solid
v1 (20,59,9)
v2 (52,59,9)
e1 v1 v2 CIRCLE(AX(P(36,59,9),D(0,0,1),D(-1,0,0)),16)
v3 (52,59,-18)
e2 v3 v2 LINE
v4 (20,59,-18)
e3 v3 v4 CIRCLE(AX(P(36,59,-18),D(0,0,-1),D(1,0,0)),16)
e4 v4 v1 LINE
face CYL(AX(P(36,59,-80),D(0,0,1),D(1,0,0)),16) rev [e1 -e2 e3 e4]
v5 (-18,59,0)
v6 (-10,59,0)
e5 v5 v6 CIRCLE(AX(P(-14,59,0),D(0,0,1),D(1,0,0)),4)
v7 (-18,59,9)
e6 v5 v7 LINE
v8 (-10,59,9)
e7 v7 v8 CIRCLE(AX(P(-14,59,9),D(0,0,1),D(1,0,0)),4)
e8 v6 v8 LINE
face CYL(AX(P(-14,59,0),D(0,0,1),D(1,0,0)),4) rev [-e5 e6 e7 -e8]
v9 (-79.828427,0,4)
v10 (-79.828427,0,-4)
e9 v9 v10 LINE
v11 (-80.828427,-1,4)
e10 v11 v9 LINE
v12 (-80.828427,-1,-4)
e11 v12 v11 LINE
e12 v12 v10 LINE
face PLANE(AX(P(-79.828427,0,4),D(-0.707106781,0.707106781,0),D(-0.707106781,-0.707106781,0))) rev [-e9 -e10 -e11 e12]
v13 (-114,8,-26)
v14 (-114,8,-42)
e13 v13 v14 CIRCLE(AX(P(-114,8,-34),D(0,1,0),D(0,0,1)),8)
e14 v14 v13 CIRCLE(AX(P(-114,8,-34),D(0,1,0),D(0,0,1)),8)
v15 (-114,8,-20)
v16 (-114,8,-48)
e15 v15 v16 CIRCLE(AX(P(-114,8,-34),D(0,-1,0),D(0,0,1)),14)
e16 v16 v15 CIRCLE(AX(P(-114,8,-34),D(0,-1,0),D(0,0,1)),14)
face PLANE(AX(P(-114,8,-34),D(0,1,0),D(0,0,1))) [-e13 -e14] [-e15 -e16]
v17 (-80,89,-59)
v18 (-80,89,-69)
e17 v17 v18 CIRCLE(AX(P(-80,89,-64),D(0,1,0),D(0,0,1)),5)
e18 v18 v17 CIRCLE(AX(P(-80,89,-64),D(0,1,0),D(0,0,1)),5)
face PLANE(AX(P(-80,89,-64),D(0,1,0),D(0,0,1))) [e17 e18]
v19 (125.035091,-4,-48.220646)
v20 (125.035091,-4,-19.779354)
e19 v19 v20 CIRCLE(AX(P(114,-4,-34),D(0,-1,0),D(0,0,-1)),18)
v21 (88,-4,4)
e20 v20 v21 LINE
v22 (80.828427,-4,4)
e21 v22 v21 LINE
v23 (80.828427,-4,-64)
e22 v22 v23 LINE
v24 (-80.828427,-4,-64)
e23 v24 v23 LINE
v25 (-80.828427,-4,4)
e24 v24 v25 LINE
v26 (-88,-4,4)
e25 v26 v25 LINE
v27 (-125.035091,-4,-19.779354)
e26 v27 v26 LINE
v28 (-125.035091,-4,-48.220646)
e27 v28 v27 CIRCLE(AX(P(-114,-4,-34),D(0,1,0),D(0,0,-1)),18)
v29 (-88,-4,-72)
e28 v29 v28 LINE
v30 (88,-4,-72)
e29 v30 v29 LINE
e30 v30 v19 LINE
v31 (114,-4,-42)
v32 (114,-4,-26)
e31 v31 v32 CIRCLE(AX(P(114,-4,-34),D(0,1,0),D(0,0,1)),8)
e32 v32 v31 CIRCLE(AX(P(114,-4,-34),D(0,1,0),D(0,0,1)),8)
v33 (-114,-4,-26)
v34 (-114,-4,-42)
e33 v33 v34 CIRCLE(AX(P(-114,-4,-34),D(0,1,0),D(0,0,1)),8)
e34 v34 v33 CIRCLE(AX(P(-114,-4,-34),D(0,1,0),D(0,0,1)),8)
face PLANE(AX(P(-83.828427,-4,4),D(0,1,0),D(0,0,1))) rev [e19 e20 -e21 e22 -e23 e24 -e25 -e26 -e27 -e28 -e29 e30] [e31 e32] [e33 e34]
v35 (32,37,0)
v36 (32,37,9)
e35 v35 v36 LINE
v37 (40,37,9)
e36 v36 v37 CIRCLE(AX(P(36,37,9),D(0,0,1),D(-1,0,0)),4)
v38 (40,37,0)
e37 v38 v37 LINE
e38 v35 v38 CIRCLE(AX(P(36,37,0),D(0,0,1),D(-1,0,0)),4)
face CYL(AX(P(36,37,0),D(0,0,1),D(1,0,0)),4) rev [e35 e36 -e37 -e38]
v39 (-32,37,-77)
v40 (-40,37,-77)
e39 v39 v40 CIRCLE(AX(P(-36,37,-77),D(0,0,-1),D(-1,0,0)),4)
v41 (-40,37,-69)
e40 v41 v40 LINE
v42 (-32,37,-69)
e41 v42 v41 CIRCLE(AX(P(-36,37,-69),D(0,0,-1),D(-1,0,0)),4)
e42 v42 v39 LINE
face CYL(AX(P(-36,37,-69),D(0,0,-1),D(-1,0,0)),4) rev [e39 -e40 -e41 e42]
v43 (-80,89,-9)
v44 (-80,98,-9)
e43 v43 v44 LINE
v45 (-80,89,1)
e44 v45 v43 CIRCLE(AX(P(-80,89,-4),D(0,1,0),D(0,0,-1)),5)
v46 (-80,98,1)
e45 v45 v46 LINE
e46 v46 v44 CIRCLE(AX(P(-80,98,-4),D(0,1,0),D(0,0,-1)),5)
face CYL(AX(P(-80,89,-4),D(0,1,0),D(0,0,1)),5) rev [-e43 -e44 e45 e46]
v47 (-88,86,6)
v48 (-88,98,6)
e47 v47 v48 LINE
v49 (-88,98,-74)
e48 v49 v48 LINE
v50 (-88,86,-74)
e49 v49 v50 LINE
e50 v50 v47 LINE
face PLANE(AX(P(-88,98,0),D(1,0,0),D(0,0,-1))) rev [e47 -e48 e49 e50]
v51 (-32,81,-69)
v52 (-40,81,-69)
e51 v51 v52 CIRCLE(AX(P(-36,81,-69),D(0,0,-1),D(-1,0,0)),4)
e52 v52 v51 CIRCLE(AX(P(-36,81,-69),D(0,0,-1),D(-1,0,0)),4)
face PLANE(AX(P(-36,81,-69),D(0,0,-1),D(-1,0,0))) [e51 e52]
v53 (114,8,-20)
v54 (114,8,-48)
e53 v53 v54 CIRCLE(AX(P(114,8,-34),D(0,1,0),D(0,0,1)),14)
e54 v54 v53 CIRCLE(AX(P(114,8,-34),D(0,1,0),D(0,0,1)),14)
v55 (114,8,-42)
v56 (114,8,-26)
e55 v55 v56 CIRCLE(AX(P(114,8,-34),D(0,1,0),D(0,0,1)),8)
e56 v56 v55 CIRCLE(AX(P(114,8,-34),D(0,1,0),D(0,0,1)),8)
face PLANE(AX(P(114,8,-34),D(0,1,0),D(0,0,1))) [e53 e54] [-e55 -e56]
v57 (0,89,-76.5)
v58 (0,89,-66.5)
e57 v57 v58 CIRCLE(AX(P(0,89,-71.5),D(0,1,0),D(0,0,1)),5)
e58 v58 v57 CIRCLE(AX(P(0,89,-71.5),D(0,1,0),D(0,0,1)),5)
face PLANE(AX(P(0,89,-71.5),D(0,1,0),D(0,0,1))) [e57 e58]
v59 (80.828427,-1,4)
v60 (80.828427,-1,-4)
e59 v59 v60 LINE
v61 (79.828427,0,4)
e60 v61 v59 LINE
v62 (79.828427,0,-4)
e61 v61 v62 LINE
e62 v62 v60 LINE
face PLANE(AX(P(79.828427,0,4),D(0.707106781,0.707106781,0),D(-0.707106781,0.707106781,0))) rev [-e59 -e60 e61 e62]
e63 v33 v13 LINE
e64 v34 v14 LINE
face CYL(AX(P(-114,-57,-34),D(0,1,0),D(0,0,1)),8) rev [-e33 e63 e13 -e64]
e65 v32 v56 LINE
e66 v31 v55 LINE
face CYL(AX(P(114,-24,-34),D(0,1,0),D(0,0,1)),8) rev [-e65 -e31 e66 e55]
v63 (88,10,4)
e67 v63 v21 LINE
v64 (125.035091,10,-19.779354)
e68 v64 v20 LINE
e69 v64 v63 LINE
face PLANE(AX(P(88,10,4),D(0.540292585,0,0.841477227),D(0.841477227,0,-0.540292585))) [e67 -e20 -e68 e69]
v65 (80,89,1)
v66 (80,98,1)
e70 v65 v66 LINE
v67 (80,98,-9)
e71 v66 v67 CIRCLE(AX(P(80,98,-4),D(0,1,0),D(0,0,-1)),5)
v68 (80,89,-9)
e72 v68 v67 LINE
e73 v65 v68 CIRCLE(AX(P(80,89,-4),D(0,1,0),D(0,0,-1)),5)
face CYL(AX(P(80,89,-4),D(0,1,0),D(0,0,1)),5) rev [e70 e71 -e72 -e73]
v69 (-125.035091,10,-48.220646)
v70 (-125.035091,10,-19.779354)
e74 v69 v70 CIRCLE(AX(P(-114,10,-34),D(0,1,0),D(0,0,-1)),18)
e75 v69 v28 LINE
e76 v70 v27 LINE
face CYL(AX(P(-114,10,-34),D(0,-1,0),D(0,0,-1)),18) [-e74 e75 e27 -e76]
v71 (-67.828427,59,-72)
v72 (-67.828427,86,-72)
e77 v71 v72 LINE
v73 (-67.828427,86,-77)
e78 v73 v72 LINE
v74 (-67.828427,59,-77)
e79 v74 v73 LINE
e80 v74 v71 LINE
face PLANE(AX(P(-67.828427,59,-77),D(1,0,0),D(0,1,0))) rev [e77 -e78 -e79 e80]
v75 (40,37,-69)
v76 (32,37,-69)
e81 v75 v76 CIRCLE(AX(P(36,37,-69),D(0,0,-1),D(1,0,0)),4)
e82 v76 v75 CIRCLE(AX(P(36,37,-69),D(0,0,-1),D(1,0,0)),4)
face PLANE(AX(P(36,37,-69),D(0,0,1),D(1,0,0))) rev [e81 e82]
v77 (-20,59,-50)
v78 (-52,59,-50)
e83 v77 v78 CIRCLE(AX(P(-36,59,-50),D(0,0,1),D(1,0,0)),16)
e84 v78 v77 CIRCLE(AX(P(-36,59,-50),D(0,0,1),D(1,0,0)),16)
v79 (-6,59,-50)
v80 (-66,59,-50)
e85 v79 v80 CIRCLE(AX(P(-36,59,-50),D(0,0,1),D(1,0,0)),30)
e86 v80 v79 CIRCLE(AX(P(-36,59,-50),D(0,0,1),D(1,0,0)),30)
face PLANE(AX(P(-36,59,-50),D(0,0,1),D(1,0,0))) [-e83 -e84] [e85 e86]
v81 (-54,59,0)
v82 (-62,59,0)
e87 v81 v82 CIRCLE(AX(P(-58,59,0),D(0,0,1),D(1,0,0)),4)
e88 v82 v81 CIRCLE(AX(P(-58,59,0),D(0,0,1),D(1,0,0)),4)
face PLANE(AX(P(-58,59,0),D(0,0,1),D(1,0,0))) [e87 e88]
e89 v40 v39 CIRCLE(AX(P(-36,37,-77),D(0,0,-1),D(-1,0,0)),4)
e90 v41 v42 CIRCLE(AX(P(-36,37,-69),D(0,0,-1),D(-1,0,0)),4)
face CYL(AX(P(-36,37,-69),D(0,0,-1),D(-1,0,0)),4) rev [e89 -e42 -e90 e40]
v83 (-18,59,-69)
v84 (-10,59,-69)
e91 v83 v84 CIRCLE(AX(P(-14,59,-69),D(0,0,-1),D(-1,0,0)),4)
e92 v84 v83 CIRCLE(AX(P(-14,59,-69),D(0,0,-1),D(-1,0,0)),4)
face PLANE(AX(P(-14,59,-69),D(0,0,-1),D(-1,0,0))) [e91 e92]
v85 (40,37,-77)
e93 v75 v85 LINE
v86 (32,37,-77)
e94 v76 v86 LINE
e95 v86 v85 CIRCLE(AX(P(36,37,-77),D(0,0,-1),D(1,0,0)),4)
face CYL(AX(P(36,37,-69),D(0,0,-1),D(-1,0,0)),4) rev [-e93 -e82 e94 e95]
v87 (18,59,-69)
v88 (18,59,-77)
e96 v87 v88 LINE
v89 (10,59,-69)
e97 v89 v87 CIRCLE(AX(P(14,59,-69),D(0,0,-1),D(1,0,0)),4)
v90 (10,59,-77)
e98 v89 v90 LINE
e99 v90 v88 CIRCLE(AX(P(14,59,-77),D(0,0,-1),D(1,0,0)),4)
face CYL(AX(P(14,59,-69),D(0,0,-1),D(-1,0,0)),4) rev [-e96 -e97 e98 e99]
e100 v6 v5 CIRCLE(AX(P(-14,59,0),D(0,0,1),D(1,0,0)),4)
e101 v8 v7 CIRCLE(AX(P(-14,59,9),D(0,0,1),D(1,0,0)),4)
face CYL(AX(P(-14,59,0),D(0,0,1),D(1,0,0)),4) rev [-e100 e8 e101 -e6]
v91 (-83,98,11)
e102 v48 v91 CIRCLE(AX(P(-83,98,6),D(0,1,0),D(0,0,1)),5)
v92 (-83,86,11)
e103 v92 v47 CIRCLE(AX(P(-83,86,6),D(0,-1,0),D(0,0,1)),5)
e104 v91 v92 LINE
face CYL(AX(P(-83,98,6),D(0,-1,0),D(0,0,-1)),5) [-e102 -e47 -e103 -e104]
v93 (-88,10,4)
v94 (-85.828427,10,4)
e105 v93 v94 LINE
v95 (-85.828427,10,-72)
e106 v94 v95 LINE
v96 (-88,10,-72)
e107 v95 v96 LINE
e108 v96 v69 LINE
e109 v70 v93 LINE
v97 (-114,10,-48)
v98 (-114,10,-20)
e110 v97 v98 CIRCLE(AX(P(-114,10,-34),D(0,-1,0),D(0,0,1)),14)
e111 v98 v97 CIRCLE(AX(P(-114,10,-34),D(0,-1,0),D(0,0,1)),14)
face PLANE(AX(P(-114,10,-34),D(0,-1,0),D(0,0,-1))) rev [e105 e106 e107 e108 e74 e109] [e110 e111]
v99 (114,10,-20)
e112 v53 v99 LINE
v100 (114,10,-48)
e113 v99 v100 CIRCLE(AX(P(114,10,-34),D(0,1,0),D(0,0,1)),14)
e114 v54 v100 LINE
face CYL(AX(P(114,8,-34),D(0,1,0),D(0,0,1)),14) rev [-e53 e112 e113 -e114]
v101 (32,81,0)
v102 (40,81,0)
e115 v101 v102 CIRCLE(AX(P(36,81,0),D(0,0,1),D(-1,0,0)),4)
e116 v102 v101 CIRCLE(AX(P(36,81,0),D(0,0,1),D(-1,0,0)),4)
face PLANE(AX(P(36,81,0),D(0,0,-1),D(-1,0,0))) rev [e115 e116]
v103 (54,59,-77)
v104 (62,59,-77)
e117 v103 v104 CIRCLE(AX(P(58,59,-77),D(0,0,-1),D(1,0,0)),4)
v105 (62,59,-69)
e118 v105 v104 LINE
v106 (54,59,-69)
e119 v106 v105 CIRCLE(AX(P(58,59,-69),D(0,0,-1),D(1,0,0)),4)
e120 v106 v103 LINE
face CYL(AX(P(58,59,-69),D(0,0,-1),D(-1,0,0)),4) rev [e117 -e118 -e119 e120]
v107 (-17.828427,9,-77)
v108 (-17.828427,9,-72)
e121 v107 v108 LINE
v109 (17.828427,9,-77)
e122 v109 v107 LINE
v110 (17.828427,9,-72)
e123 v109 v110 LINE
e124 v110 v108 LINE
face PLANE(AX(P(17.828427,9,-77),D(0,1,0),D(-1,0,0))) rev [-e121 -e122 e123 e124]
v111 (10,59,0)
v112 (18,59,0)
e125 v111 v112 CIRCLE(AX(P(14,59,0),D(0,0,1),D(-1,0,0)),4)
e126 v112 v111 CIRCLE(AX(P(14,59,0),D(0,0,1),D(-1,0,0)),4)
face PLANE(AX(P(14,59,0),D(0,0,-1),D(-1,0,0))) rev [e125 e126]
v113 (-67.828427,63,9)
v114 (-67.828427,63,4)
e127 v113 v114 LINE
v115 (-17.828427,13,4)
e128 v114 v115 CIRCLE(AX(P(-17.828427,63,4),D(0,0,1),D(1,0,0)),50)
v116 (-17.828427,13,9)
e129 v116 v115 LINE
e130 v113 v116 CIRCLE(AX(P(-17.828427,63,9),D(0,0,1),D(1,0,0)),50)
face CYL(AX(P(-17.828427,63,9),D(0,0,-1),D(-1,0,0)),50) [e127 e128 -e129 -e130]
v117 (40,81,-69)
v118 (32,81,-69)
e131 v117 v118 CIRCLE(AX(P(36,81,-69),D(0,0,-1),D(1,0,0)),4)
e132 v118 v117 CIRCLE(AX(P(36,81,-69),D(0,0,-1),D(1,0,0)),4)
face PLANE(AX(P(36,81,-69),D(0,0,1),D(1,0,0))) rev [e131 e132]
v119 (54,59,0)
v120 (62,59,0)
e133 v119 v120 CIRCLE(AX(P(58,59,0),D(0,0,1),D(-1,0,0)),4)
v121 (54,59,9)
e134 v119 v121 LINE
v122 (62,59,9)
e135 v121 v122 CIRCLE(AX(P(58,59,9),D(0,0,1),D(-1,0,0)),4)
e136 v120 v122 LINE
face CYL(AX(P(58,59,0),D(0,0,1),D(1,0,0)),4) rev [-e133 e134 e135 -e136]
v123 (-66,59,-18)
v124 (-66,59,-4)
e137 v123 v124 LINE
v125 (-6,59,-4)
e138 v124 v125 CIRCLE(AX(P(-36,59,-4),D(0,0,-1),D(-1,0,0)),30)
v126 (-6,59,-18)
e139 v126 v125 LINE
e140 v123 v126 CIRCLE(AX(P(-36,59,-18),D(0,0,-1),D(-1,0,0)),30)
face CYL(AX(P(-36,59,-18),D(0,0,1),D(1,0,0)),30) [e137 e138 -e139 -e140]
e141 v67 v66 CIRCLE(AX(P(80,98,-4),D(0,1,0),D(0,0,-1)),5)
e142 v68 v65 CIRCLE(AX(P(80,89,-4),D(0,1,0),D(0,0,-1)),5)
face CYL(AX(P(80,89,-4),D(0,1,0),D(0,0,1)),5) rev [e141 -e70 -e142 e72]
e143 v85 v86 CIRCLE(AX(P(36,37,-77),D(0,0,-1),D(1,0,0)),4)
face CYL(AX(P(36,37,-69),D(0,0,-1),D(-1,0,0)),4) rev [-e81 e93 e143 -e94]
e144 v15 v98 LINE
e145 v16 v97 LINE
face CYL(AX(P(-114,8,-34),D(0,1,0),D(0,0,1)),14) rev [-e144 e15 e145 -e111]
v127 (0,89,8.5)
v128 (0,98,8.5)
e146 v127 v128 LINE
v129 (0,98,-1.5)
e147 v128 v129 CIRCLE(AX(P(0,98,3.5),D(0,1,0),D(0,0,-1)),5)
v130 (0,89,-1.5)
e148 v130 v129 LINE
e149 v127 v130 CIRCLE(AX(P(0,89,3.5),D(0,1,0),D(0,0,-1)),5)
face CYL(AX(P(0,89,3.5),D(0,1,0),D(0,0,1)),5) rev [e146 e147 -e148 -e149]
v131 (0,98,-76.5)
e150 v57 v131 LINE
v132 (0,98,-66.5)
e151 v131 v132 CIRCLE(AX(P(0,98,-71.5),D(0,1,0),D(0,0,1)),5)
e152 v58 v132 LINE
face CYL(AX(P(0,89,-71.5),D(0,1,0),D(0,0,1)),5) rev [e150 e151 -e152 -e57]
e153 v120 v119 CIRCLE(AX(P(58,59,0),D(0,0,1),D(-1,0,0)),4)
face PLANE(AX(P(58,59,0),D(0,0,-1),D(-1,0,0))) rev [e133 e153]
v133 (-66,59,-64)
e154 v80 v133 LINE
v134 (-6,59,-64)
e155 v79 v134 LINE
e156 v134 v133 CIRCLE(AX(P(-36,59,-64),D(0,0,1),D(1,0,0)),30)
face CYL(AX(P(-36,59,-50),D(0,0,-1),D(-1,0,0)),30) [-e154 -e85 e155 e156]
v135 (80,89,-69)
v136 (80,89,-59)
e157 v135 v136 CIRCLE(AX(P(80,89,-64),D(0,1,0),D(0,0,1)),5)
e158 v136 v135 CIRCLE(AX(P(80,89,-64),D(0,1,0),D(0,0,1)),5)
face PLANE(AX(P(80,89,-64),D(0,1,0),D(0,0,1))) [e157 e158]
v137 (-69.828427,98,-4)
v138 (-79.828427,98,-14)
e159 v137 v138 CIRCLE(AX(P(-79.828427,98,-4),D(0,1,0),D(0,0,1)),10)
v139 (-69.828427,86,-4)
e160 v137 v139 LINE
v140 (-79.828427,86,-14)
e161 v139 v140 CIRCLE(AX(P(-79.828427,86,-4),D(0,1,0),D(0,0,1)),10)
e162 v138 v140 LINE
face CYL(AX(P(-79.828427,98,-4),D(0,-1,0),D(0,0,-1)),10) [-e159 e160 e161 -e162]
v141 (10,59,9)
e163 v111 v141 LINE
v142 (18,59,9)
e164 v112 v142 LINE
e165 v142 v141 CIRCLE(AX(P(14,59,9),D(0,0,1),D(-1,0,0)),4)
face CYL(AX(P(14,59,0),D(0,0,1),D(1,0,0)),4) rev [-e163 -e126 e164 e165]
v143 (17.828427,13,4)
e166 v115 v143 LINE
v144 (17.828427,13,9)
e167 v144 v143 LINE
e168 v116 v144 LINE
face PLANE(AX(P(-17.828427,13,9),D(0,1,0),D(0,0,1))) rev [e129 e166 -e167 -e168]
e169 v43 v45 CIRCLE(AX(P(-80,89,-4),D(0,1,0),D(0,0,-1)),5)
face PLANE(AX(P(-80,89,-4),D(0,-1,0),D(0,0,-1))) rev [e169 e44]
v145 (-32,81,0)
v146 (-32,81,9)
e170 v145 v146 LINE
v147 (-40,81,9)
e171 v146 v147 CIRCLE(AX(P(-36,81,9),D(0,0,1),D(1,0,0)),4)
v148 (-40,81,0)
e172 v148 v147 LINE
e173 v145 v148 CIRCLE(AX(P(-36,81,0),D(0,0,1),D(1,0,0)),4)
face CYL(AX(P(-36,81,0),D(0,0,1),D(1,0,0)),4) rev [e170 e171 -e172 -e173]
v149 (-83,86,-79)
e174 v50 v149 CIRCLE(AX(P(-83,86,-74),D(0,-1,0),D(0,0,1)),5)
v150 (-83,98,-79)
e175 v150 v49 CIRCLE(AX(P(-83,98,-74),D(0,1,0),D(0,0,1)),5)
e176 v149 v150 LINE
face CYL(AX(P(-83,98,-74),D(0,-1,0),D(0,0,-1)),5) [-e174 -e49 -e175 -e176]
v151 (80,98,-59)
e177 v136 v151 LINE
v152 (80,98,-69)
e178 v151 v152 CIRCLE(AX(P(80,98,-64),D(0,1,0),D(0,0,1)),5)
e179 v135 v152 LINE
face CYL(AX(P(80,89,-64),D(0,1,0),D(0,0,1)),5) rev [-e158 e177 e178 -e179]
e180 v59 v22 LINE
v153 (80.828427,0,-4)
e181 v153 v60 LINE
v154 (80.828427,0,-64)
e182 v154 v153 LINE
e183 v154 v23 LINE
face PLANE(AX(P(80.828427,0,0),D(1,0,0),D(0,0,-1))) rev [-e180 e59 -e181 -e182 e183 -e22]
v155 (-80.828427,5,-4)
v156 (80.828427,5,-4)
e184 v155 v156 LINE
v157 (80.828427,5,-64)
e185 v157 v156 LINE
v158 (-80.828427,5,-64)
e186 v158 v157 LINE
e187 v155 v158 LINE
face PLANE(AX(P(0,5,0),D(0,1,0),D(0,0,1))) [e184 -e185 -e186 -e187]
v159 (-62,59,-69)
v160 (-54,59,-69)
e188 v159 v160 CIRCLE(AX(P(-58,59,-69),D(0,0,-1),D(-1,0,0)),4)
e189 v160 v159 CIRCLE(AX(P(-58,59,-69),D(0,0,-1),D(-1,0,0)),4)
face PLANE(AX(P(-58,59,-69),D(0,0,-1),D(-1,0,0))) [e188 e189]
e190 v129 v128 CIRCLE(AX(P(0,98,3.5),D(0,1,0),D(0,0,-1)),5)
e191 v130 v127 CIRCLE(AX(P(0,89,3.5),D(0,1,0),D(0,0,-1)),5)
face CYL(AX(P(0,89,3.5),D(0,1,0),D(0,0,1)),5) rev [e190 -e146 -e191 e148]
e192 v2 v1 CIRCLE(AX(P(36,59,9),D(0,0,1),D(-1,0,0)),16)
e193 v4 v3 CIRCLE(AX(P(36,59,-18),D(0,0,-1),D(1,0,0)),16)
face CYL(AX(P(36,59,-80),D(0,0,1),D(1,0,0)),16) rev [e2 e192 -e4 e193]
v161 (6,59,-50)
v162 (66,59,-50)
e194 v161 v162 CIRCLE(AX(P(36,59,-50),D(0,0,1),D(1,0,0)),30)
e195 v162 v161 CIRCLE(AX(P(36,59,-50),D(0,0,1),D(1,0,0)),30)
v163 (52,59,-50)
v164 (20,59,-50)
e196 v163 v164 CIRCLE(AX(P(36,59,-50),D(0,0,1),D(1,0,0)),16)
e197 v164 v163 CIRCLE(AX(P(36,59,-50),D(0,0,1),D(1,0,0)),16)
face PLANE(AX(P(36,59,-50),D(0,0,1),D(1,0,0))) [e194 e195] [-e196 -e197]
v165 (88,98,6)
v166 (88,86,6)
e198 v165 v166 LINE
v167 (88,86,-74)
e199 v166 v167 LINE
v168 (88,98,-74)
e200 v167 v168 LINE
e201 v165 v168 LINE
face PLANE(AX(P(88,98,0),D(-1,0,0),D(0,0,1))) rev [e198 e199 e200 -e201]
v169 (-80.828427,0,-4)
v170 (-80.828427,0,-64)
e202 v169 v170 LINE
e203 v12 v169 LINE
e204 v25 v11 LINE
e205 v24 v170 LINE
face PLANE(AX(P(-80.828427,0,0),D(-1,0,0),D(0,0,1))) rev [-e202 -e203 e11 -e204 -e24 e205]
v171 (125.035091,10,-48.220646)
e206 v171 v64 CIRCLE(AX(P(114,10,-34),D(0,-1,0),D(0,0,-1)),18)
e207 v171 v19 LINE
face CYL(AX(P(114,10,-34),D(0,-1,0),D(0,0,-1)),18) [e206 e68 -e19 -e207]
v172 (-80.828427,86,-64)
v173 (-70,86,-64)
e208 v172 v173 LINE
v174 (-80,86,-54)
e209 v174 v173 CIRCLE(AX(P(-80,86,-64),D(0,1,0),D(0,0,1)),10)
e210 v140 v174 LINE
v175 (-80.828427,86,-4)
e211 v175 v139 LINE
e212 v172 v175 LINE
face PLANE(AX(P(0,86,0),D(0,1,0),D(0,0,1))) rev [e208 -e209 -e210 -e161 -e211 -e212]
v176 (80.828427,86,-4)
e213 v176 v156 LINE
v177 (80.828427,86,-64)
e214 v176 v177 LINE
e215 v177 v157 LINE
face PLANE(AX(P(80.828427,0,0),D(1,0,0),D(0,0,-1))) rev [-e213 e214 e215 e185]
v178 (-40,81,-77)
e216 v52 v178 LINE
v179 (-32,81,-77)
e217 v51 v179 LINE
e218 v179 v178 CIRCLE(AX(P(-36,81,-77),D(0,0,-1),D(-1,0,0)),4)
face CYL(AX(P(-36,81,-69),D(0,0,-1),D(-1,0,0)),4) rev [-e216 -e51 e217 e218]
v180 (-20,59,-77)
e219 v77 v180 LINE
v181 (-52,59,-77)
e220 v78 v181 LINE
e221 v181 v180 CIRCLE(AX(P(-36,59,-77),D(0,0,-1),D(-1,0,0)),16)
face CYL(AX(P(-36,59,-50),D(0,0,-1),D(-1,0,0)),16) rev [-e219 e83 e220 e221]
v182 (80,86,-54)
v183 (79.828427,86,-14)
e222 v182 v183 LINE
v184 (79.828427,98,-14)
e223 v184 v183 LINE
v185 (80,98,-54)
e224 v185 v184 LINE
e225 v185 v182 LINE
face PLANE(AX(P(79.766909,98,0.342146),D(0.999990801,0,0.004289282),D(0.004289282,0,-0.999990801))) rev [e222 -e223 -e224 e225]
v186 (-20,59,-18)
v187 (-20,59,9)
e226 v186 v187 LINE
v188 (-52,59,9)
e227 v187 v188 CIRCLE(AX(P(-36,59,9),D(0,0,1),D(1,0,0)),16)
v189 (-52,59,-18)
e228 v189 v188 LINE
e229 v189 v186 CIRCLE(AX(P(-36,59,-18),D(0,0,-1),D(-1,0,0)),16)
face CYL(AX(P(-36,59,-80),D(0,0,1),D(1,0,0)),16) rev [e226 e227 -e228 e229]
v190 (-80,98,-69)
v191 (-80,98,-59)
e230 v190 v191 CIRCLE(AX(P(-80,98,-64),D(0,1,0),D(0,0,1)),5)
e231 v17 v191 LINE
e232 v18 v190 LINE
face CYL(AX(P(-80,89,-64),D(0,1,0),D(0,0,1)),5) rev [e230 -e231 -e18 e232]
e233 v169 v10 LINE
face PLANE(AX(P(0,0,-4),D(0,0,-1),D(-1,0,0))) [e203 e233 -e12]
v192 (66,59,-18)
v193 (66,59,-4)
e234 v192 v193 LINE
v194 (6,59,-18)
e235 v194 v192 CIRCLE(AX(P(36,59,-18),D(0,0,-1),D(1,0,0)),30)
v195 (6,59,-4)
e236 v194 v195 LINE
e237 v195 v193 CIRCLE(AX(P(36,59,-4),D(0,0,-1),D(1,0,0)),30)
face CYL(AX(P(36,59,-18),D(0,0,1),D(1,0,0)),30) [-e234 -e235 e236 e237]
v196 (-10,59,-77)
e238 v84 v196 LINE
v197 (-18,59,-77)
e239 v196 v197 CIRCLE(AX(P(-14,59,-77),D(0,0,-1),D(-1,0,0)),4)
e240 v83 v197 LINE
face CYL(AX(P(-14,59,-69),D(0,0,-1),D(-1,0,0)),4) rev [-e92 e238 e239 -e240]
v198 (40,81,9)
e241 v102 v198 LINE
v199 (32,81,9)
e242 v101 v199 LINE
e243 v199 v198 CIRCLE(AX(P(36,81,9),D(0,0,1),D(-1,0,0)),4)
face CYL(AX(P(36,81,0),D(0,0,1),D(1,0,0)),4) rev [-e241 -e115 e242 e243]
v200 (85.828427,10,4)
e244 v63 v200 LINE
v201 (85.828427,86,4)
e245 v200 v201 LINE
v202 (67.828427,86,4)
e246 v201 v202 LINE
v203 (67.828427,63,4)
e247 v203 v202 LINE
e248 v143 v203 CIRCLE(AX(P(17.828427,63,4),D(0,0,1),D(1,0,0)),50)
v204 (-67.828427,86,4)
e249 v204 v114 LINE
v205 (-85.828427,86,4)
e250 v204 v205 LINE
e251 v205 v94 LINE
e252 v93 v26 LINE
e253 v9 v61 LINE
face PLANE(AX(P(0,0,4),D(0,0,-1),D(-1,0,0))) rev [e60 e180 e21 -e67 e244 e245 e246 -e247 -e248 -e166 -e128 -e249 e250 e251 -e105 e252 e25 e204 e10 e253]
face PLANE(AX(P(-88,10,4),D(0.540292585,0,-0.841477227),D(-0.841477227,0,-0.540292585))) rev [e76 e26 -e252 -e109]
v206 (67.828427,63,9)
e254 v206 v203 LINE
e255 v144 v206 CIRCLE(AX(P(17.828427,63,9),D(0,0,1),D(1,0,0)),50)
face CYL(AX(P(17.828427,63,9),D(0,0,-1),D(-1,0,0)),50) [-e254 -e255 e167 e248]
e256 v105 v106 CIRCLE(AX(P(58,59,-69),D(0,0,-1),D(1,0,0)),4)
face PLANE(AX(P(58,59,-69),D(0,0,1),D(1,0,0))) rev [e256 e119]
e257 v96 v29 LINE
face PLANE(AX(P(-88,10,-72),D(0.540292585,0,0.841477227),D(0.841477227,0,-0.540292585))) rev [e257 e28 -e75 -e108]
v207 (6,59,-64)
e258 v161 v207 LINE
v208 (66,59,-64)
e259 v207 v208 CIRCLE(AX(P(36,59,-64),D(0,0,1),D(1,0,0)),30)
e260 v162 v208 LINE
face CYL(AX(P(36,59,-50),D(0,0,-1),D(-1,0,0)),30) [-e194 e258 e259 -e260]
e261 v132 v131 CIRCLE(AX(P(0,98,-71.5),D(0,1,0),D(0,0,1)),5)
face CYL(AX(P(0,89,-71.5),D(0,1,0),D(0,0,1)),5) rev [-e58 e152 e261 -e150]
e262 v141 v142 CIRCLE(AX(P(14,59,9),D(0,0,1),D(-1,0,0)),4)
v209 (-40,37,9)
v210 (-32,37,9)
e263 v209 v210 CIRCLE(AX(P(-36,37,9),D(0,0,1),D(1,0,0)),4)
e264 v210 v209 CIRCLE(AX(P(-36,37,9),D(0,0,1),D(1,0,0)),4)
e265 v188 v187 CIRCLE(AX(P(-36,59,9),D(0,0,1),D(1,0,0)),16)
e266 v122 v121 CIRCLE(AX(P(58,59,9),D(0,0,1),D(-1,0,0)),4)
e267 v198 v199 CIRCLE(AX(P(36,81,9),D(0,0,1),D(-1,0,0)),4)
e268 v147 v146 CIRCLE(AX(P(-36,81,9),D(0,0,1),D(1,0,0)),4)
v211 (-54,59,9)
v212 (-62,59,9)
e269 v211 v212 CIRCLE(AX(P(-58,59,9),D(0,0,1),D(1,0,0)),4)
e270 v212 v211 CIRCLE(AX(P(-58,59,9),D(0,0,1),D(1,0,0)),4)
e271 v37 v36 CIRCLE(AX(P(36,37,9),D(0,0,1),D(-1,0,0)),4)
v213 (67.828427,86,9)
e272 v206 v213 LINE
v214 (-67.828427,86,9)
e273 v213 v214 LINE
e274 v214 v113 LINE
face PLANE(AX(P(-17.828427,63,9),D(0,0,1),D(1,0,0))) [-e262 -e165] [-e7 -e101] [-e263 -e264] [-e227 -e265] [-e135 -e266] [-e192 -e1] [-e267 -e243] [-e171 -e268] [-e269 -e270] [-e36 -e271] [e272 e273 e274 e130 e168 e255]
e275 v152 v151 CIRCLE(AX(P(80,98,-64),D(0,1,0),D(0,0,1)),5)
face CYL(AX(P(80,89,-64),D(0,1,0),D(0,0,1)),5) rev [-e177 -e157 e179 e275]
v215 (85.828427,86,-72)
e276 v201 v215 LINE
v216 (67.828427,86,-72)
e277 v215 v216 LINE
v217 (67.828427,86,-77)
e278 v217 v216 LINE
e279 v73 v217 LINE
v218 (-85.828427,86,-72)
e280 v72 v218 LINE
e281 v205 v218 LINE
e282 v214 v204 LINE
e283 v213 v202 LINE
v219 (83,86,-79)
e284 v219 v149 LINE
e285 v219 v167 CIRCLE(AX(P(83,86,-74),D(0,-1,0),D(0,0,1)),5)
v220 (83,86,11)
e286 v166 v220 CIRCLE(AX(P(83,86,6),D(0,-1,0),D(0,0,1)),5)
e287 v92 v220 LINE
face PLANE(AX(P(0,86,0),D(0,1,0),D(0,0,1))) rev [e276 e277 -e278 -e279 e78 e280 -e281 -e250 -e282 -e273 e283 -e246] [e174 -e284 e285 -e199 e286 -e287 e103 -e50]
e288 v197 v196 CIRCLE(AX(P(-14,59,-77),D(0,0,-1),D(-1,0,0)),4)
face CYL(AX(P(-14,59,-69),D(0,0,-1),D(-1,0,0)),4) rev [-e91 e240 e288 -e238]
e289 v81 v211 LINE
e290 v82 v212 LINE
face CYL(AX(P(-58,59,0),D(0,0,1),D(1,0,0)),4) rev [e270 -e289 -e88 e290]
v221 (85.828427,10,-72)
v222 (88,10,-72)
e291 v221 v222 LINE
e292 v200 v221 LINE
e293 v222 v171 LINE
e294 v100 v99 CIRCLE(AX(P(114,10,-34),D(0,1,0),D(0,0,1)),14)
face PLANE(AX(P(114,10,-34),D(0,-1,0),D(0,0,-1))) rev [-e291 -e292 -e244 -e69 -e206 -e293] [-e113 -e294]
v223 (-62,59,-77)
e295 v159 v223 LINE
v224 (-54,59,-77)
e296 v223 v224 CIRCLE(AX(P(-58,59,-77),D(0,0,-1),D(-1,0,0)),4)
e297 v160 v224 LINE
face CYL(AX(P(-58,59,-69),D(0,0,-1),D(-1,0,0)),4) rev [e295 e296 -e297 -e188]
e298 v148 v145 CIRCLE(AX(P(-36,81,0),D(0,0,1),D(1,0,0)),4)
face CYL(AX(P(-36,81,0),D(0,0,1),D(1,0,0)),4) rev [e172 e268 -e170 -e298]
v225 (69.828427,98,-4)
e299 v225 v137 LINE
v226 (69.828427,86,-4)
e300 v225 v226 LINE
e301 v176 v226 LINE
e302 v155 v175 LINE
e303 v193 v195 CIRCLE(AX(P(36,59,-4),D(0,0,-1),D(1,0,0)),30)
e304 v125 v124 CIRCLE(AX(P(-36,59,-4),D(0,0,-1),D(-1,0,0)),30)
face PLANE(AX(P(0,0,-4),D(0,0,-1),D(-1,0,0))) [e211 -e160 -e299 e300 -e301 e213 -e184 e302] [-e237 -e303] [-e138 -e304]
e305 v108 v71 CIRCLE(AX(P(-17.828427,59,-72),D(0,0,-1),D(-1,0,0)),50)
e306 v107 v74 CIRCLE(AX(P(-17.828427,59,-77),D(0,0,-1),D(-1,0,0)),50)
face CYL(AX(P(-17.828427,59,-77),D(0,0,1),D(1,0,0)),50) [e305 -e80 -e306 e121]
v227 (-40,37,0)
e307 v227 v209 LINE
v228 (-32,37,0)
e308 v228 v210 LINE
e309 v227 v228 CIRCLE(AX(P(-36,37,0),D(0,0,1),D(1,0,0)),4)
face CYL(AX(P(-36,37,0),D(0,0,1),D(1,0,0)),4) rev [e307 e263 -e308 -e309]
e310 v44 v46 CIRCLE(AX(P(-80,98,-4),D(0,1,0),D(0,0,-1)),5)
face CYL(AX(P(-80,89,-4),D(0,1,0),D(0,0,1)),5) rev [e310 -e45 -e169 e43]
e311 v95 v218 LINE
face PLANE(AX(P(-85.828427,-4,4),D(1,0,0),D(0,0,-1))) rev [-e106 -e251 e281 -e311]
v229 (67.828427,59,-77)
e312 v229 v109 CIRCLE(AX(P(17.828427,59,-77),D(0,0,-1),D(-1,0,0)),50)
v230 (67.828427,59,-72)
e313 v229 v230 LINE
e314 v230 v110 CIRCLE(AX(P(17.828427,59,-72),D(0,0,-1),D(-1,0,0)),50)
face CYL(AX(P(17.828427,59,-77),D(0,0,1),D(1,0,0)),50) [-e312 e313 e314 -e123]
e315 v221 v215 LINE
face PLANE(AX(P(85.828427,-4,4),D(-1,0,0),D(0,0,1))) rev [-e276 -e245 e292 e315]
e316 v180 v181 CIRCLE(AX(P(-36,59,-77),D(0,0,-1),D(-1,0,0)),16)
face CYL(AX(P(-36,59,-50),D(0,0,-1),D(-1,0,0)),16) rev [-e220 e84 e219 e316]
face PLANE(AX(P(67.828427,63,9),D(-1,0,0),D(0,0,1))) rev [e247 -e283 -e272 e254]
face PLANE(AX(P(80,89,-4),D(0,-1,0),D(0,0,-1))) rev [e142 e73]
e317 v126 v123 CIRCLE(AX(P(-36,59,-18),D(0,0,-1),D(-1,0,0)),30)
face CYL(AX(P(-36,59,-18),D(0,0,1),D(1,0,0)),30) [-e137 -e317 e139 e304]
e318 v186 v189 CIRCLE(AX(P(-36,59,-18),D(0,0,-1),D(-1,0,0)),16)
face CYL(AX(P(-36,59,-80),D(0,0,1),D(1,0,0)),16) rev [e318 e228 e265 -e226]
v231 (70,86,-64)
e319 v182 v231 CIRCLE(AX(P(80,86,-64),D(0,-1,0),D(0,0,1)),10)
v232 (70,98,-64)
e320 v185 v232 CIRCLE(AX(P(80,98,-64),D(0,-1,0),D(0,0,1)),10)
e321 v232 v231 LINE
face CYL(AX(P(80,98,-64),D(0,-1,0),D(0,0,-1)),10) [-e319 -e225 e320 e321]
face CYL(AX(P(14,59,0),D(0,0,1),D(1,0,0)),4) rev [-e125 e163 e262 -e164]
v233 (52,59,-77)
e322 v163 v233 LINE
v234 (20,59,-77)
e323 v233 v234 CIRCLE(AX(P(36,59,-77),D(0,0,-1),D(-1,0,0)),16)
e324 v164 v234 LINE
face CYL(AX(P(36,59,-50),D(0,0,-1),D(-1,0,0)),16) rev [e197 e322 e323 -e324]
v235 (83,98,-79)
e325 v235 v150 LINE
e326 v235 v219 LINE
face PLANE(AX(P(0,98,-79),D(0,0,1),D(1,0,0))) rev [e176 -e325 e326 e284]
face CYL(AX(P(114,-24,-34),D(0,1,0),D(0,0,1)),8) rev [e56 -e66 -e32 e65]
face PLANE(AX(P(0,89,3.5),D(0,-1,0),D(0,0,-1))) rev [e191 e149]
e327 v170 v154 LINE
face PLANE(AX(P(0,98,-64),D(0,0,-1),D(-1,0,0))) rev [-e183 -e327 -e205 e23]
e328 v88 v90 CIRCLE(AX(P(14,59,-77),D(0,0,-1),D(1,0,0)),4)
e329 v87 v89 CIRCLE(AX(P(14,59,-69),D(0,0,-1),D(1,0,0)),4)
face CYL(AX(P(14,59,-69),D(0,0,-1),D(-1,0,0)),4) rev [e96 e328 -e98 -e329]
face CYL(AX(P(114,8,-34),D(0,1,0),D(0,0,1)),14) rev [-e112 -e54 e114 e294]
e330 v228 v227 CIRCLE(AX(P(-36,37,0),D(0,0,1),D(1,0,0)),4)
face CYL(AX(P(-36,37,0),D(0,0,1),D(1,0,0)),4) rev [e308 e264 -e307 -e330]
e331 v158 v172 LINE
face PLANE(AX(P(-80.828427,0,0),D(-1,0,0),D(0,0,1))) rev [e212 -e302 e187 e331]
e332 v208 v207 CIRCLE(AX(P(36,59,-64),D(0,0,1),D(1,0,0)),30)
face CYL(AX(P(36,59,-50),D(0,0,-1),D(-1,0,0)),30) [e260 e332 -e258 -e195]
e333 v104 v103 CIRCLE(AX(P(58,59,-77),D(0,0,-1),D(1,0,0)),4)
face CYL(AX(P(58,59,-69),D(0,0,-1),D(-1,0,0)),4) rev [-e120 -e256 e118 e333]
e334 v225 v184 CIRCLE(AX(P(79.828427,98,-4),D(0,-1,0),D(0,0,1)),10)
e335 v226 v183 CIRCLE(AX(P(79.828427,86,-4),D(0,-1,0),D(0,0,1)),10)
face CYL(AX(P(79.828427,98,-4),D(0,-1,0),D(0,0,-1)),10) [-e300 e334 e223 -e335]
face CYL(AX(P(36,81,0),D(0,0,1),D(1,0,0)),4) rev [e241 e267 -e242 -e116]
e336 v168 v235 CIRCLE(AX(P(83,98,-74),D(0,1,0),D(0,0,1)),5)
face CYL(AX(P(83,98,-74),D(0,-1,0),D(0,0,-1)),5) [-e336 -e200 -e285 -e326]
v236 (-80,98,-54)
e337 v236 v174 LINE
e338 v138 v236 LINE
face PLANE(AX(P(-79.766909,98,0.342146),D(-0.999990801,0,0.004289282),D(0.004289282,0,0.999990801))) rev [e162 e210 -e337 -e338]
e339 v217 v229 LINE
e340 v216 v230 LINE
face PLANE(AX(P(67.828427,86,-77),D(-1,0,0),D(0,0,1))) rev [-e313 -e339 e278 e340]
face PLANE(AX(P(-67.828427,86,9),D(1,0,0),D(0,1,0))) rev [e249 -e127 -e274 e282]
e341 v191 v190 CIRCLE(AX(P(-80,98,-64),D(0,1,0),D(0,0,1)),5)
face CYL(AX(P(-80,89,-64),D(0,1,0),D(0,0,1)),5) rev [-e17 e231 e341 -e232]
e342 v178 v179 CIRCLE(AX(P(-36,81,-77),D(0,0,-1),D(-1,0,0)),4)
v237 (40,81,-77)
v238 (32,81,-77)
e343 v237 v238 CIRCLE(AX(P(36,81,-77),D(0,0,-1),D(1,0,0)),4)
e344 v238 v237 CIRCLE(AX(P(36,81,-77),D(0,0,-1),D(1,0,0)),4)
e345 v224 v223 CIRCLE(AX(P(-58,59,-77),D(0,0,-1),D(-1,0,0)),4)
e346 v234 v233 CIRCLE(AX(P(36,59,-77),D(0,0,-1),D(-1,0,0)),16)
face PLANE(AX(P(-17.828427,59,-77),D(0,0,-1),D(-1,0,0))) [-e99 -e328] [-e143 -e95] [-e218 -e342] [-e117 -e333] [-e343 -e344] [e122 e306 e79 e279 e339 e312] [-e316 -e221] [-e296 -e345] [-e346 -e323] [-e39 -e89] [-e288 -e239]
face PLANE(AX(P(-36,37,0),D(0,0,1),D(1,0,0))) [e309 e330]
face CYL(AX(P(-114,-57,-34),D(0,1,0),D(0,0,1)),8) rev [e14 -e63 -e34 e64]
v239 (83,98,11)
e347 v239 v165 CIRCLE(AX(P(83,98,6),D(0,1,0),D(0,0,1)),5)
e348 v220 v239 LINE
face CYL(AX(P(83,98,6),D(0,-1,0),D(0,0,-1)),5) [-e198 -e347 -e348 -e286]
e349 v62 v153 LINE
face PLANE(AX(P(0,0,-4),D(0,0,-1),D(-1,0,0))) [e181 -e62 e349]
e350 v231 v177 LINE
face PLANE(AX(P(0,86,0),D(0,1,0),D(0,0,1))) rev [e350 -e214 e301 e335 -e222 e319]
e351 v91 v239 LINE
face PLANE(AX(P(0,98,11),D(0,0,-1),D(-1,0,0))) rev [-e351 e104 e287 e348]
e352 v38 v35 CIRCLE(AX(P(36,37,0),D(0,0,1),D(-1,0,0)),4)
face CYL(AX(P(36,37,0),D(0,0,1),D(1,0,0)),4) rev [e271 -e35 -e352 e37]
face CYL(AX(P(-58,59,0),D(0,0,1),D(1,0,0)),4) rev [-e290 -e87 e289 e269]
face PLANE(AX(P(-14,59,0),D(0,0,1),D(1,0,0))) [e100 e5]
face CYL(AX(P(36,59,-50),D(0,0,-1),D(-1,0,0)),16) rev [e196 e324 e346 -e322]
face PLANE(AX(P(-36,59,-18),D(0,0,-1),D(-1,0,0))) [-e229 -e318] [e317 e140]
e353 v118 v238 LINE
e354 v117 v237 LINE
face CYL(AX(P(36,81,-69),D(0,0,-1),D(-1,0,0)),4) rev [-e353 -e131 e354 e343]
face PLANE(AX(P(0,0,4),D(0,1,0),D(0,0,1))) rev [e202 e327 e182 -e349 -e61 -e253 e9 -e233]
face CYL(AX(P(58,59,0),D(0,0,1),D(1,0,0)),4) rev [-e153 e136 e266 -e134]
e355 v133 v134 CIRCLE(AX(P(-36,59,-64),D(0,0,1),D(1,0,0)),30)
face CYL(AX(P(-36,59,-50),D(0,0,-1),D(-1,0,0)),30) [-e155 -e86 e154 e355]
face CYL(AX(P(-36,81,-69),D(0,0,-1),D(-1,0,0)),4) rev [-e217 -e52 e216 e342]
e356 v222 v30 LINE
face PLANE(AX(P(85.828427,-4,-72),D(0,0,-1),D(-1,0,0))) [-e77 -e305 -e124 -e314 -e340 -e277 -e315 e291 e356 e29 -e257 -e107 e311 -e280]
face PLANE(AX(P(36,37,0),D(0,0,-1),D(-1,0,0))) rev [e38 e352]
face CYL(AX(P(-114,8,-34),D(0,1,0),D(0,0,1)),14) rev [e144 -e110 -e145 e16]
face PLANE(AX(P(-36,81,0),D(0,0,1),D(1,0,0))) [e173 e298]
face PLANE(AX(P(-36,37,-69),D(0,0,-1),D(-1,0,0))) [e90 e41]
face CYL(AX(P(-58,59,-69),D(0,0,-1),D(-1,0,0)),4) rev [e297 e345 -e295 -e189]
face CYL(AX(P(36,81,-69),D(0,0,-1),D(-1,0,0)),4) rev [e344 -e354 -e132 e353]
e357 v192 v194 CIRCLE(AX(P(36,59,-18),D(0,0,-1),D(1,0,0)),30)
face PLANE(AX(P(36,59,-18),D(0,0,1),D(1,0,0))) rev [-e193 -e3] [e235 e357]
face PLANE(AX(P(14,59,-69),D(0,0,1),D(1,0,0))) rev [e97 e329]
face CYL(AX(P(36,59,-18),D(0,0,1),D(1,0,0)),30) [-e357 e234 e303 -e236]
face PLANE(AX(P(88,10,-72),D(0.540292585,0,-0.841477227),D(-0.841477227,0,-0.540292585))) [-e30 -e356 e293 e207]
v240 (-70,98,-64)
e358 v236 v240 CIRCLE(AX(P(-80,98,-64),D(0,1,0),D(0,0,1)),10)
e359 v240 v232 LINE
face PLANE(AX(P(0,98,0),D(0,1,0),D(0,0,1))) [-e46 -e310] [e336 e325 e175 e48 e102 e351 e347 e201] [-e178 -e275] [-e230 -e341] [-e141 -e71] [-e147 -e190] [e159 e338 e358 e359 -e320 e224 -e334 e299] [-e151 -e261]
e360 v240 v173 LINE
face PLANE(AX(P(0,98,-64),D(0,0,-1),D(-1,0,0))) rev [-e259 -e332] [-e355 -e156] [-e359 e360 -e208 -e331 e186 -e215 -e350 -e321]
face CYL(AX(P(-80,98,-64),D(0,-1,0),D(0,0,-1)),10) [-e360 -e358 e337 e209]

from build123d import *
from build123d.topology import SkipClean

# Parameters (mm, degrees)
FRONT_WALL_DEPTH                = 4
FRONT_BEARING_BOSSES_DEPTH      = 5
BEARING_BORE_SKETCH_R           = 16
BEARING_BORES_2X_32_DEPTH       = 89
FRONT_BEARING_HUB_SKETCH_R      = 30
FRONT_BEARING_HUB_SKETCH_R_2    = 16
FRONT_BEARING_HUBS_DEPTH        = 14
FRONT_COVER_SCREW_HOLE_SKETCH_R = 4
FRONT_COVER_SCREW_HOLES_DEPTH   = 9
HOUSING_WALL_SKETCH_W           = 171.65685425
HOUSING_WALL_SKETCH_H           = 8
HOUSING_WALLS_DEPTH             = 90
REAR_BEARING_BOSSES_DEPTH       = 5
REAR_START                      = 14
REAR_BEARING_HUB_SKETCH_R       = 30
REAR_BEARING_HUB_SKETCH_R_2     = 16
REAR_BEARING_HUBS_DEPTH         = 14
REAR_BEARING_BORE_SKETCH_R      = 16
REAR_BEARING_BORES_DEPTH        = 98
REAR_START_2                    = -8
REAR_COVER_SCREW_HOLE_SKETCH_R  = 4
REAR_COVER_SCREW_HOLES_DEPTH    = 8
TOP_COVER_FLANGE_SKETCH_W       = 176
TOP_COVER_FLANGE_SKETCH_H       = 90
TOP_COVER_FLANGE_DEPTH          = 12
WALL_INFILL_1_SKETCH_W          = 76
WALL_INFILL_1_SKETCH_H          = 102
WALL_INFILL_1_DEPTH             = 5
WALL_INFILL_2_SKETCH_W          = 76
WALL_INFILL_2_SKETCH_H          = 102
WALL_INFILL_2_DEPTH             = 5
FLANGE_SCREW_HOLE_SKETCH_R      = 5
FLANGE_SCREW_HOLES_DEPTH        = 9
FLANGE_CORNER_FILLET_R5_A_R     = 5
FLANGE_CORNER_FILLET_R5_B_R     = 5
FLANGE_CORNER_FILLET_R5_C_R     = 5
FLANGE_CORNER_FILLET_R5_D_R     = 5
MOUNTING_LUG_DEPTH              = 14
WALL_INFILL_3_SKETCH_W          = 161.65685425
WALL_INFILL_3_SKETCH_H          = 68
WALL_INFILL_3_DEPTH             = 5
LUG_SPOTFACE_SKETCH_R           = 14
LUG_SPOTFACE_28_DEPTH           = 2
LUG_BOLT_HOLE_SKETCH_R          = 8
LUG_BOLT_HOLE_DEPTH             = 32
MIRRORED_LUG_BOLT_HOLE_SKETCH_R = 8
MIRRORED_LUG_BOLT_HOLE_DEPTH    = 65


with BuildPart() as part:
    # Front Wall Sketch → Front Wall (new, symmetric)
    with BuildSketch(Plane.XY):
        Polygon((0, 0), (79.828427125, 0), (83.828427125, -4), (85.828427125, -4), (85.828427125, 86), (-85.828427125, 86), (-85.828427125, -4), (-83.828427125, -4), (-79.828427125, 0), align=None)
    extrude(amount=FRONT_WALL_DEPTH, both=True)

    # Front Bearing Boss Sketch → Front Bearing Bosses (add)
    with BuildSketch(Plane.XY.offset(4)):
        with BuildLine():
            Line((-67.828427125, 86), (67.828427125, 86))
            Line((67.828427125, 86), (67.828427125, 63))
            ThreePointArc((67.828427125, 63), (53.183766184, 27.644660941), (17.828427125, 13))
            Line((17.828427125, 13), (-17.828427125, 13))
            ThreePointArc((-17.828427125, 13), (-53.183766184, 27.644660941), (-67.828427125, 63))
            Line((-67.828427125, 63), (-67.828427125, 86))
        make_face()
    extrude(amount=FRONT_BEARING_BOSSES_DEPTH)

    # Bearing Bore Sketch → Bearing Bores 2x_32 (cut)
    with BuildSketch(Plane.XY.offset(9)):
        with Locations((-36, 59)):
            Circle(BEARING_BORE_SKETCH_R)
        with Locations(Location((36, 59, 0), (0, 0, 180))):
            Circle(BEARING_BORE_SKETCH_R)
    extrude(amount=-BEARING_BORES_2X_32_DEPTH, mode=Mode.SUBTRACT)

    # Front Bearing Hub Sketch → Front Bearing Hubs (add)
    # profile 1 of 2: a face of its own
    with SkipClean():  # the faces are left unmerged after this step: merging them gives an invalid solid
        with BuildSketch(Plane(origin=(0, 0, -4), x_dir=(-1, 0, 0), z_dir=(0, 0, -1))):
            with Locations(Location((36, 59, 0), (0, 0, 115.841932763))):
                Circle(FRONT_BEARING_HUB_SKETCH_R)
            with Locations(Location((36, 59, 0), (0, 0, 180))):
                Circle(FRONT_BEARING_HUB_SKETCH_R_2, mode=Mode.SUBTRACT)
        # profile 2 of 2: a face of its own
        with BuildSketch(Plane(origin=(0, 0, -4), x_dir=(-1, 0, 0), z_dir=(0, 0, -1))):
            with Locations(Location((-36, 59, 0), (0, 0, 180))):
                Circle(FRONT_BEARING_HUB_SKETCH_R)
            with Locations(Location((-36, 59, 0), (0, 0, 180))):
                Circle(FRONT_BEARING_HUB_SKETCH_R_2, mode=Mode.SUBTRACT)
        extrude(amount=FRONT_BEARING_HUBS_DEPTH)

    # Front Cover Screw Hole Sketch → Front Cover Screw Holes (cut)
    with SkipClean():  # the faces are left unmerged after this step: merging them gives an invalid solid
        with BuildSketch(Plane.XY.offset(9)):
            with Locations((-36, 81)):
                Circle(FRONT_COVER_SCREW_HOLE_SKETCH_R)
            with Locations((-14, 59)):
                Circle(FRONT_COVER_SCREW_HOLE_SKETCH_R)
            with Locations((-36, 37)):
                Circle(FRONT_COVER_SCREW_HOLE_SKETCH_R)
            with Locations((-58, 59)):
                Circle(FRONT_COVER_SCREW_HOLE_SKETCH_R)
            with Locations(Location((36, 37, 0), (0, 0, 180))):
                Circle(FRONT_COVER_SCREW_HOLE_SKETCH_R)
            with Locations(Location((58, 59, 0), (0, 0, 180))):
                Circle(FRONT_COVER_SCREW_HOLE_SKETCH_R)
            with Locations(Location((36, 81, 0), (0, 0, 180))):
                Circle(FRONT_COVER_SCREW_HOLE_SKETCH_R)
            with Locations(Location((14, 59, 0), (0, 0, 180))):
                Circle(FRONT_COVER_SCREW_HOLE_SKETCH_R)
        extrude(amount=-FRONT_COVER_SCREW_HOLES_DEPTH, mode=Mode.SUBTRACT)



with BuildPart() as body_2:
    # Housing Wall Sketch → Housing Walls (new body)
    with BuildSketch(Plane(origin=(0, 86, 0), x_dir=(1, 0, 0), z_dir=(0, 1, 0))):
        with Locations((0, 68)):
            Rectangle(HOUSING_WALL_SKETCH_W, HOUSING_WALL_SKETCH_H)
    extrude(amount=-HOUSING_WALLS_DEPTH)

    # Rear Bearing Boss Sketch → Rear Bearing Bosses (add)
    with BuildSketch(Plane(origin=(0, 0, -72), x_dir=(-1, 0, 0), z_dir=(0, 0, -1))):
        with BuildLine():
            Line((-67.828427125, 86), (-67.828427125, 59))
            ThreePointArc((-67.828427125, 59), (-53.183766184, 23.644660941), (-17.828427125, 9))
            Line((-17.828427125, 9), (17.828427125, 9))
            ThreePointArc((17.828427125, 9), (53.183766184, 23.644660941), (67.828427125, 59))
            Line((67.828427125, 59), (67.828427125, 86))
            Line((67.828427125, 86), (-67.828427125, 86))
        make_face()
    extrude(amount=REAR_BEARING_BOSSES_DEPTH)

    # Rear Bearing Hub Sketch → Rear Bearing Hubs (add)
    # profile 1 of 2: a face of its own
    with BuildSketch(Plane.XY.offset(-64).offset(REAR_START)):
        with Locations((36, 59)):
            Circle(REAR_BEARING_HUB_SKETCH_R)
        with Locations((36, 59)):
            Circle(REAR_BEARING_HUB_SKETCH_R_2, mode=Mode.SUBTRACT)
    # profile 2 of 2: a face of its own
    with BuildSketch(Plane.XY.offset(-64).offset(REAR_START)):
        with Locations(Location((-36, 59, 0), (0, 0, 64.158067237))):
            Circle(REAR_BEARING_HUB_SKETCH_R)
        with Locations((-36, 59)):
            Circle(REAR_BEARING_HUB_SKETCH_R_2, mode=Mode.SUBTRACT)
    extrude(amount=-REAR_BEARING_HUBS_DEPTH)

    # Rear Bearing Bore Sketch → Rear Bearing Bores (cut)
    with BuildSketch(Plane.XY.offset(-64)):
        with Locations((36, 59)):
            Circle(REAR_BEARING_BORE_SKETCH_R)
        with Locations((-36, 59)):
            Circle(REAR_BEARING_BORE_SKETCH_R)
    extrude(amount=-REAR_BEARING_BORES_DEPTH, mode=Mode.SUBTRACT)

    # Rear Cover Screw Hole Sketch → Rear Cover Screw Holes (cut)
    with BuildSketch(Plane(origin=(0, 0, -77), x_dir=(-1, 0, 0), z_dir=(0, 0, -1)).offset(REAR_START_2)):
        with Locations(Location((36, 81, 0), (0, 0, 180))):
            Circle(REAR_COVER_SCREW_HOLE_SKETCH_R)
        with Locations(Location((58, 59, 0), (0, 0, 180))):
            Circle(REAR_COVER_SCREW_HOLE_SKETCH_R)
        with Locations(Location((36, 37, 0), (0, 0, 180))):
            Circle(REAR_COVER_SCREW_HOLE_SKETCH_R)
        with Locations(Location((14, 59, 0), (0, 0, 180))):
            Circle(REAR_COVER_SCREW_HOLE_SKETCH_R)
        with Locations((-14, 59)):
            Circle(REAR_COVER_SCREW_HOLE_SKETCH_R)
        with Locations((-36, 37)):
            Circle(REAR_COVER_SCREW_HOLE_SKETCH_R)
        with Locations((-58, 59)):
            Circle(REAR_COVER_SCREW_HOLE_SKETCH_R)
        with Locations((-36, 81)):
            Circle(REAR_COVER_SCREW_HOLE_SKETCH_R)
    extrude(amount=REAR_COVER_SCREW_HOLES_DEPTH, mode=Mode.SUBTRACT)


with BuildPart() as part_1:
    with SkipClean():  # the faces are left unmerged after this step: merging them gives an invalid solid
        add(part.part)

        add(body_2.part)  # Top Cover Flange merges body 2
        # Top Cover Flange Sketch → Top Cover Flange (add)
        with BuildSketch(Plane(origin=(0, 86, 0), x_dir=(1, 0, 0), z_dir=(0, 1, 0))):
            with Locations((0, 34)):
                Rectangle(TOP_COVER_FLANGE_SKETCH_W, TOP_COVER_FLANGE_SKETCH_H)
            with BuildLine():
                Line((-69.828427125, 4), (69.828427125, 4))
                ThreePointArc((69.828427125, 4), (72.757359313, 11.071067812), (79.828427125, 14))
                Line((79.828427125, 14), (80, 54))
                ThreePointArc((80, 54), (72.928932188, 56.928932188), (70, 64))
                Line((70, 64), (-70, 64))
                ThreePointArc((-70, 64), (-72.928932188, 56.928932188), (-80, 54))
                Line((-80, 54), (-79.828427125, 14))
                ThreePointArc((-79.828427125, 14), (-72.757359313, 11.071067812), (-69.828427125, 4))
            make_face(mode=Mode.SUBTRACT)
        extrude(amount=TOP_COVER_FLANGE_DEPTH)

    # Wall Infill 1 Sketch → Wall Infill 1 (add)
    with SkipClean():  # the faces are left unmerged after this step: merging them gives an invalid solid
        with BuildSketch(Plane(origin=(85.828427125, 0, 0), x_dir=(0, 0, -1), z_dir=(1, 0, 0))):
            with Locations((34, 47)):
                Rectangle(WALL_INFILL_1_SKETCH_W, WALL_INFILL_1_SKETCH_H)
        extrude(amount=-WALL_INFILL_1_DEPTH)

    # Wall Infill 2 Sketch → Wall Infill 2 (add)
    with SkipClean():  # the faces are left unmerged after this step: merging them gives an invalid solid
        with BuildSketch(Plane.ZY.offset(85.828427125)):
            with Locations((-34, 47)):
                Rectangle(WALL_INFILL_2_SKETCH_W, WALL_INFILL_2_SKETCH_H)
        extrude(amount=-WALL_INFILL_2_DEPTH)

    # Flange Screw Hole Sketch → Flange Screw Holes (cut)
    with SkipClean():  # the faces are left unmerged after this step: merging them gives an invalid solid
        with BuildSketch(Plane(origin=(0, 98, 0), x_dir=(1, 0, 0), z_dir=(0, 1, 0))):
            with Locations(Location((-80, 64, 0), (0, 0, 270))):
                Circle(FLANGE_SCREW_HOLE_SKETCH_R)
            with Locations(Location((0, 71.5, 0), (0, 0, 270))):
                Circle(FLANGE_SCREW_HOLE_SKETCH_R)
            with Locations(Location((80, 64, 0), (0, 0, 270))):
                Circle(FLANGE_SCREW_HOLE_SKETCH_R)
            with Locations(Location((-80, 4, 0), (0, 0, 90))):
                Circle(FLANGE_SCREW_HOLE_SKETCH_R)
            with Locations(Location((0, -3.5, 0), (0, 0, 90))):
                Circle(FLANGE_SCREW_HOLE_SKETCH_R)
            with Locations(Location((80, 4, 0), (0, 0, 90))):
                Circle(FLANGE_SCREW_HOLE_SKETCH_R)
        extrude(amount=-FLANGE_SCREW_HOLES_DEPTH, mode=Mode.SUBTRACT)

    # Flange Corner Fillet R5 A
    flange_corner_fillet_r5_a_edges = [part_1.edges().sort_by_distance(p)[0] for p in [
        (88, 92, 11),
    ]]
    fillet(flange_corner_fillet_r5_a_edges, radius=FLANGE_CORNER_FILLET_R5_A_R)

    # Flange Corner Fillet R5 B
    flange_corner_fillet_r5_b_edges = [part_1.edges().sort_by_distance(p)[0] for p in [
        (88, 92, -79),
    ]]
    fillet(flange_corner_fillet_r5_b_edges, radius=FLANGE_CORNER_FILLET_R5_B_R)

    # Flange Corner Fillet R5 C
    flange_corner_fillet_r5_c_edges = [part_1.edges().sort_by_distance(p)[0] for p in [
        (-88, 92, 11),
    ]]
    fillet(flange_corner_fillet_r5_c_edges, radius=FLANGE_CORNER_FILLET_R5_C_R)

    # Flange Corner Fillet R5 D
    flange_corner_fillet_r5_d_edges = [part_1.edges().sort_by_distance(p)[0] for p in [
        (-88, 92, -79),
    ]]
    fillet(flange_corner_fillet_r5_d_edges, radius=FLANGE_CORNER_FILLET_R5_D_R)

    # Mounting Lug Sketch → Mounting Lug (add)
    with SkipClean():  # the faces are left unmerged after this step: merging them gives an invalid solid
        with BuildSketch(Plane.XZ.offset(4)):
            with BuildLine():
                Line((88, -72), (85.828427125, -72))
                Line((85.828427125, -72), (85.828427125, 4))
                Line((85.828427125, 4), (88, 4))
                Line((88, 4), (125.035091127, -19.779354311))
                ThreePointArc((125.035091127, -19.779354311), (132, -34), (125.035091127, -48.220645689))
                Line((125.035091127, -48.220645689), (88, -72))
            make_face()
        mounting_lug = extrude(amount=-MOUNTING_LUG_DEPTH)

    # Wall Infill 3 Sketch → Wall Infill 3 (add)
    with SkipClean():  # the faces are left unmerged after this step: merging them gives an invalid solid
        with BuildSketch(Plane.XZ):
            with Locations((0, -30)):
                Rectangle(WALL_INFILL_3_SKETCH_W, WALL_INFILL_3_SKETCH_H)
        extrude(amount=-WALL_INFILL_3_DEPTH)

    # Lug Spotface Sketch → Lug Spotface _28 (cut)
    with SkipClean():  # the faces are left unmerged after this step: merging them gives an invalid solid
        with BuildSketch(Plane(origin=(0, 10, 0), x_dir=(1, 0, 0), z_dir=(0, 1, 0))):
            with Locations(Location((114, 34, 0), (0, 0, 270))):
                Circle(LUG_SPOTFACE_SKETCH_R)
        lug_spotface_28 = extrude(amount=-LUG_SPOTFACE_28_DEPTH, mode=Mode.SUBTRACT)

    # Lug Bolt Hole Sketch → Lug Bolt Hole (cut)
    with SkipClean():  # the faces are left unmerged after this step: merging them gives an invalid solid
        with BuildSketch(Plane(origin=(0, 8, 0), x_dir=(1, 0, 0), z_dir=(0, 1, 0))):
            with Locations(Location((114, 34, 0), (0, 0, 270))):
                Circle(LUG_BOLT_HOLE_SKETCH_R)
        extrude(amount=-LUG_BOLT_HOLE_DEPTH, mode=Mode.SUBTRACT)

    # Mounting Lug Mirror: Mounting Lug, Lug Spotface _28 across plane
    with SkipClean():  # the faces are left unmerged after this step: merging them gives an invalid solid
        add(mounting_lug.mirror(Plane(origin=(0, 0, 0), x_dir=(0, 0, 1), z_dir=(1, 0, 0))))
        add(lug_spotface_28.mirror(Plane(origin=(0, 0, 0), x_dir=(0, 0, 1), z_dir=(1, 0, 0))), mode=Mode.SUBTRACT)

    # Mirrored Lug Bolt Hole Sketch → Mirrored Lug Bolt Hole (cut)
    with SkipClean():  # the faces are left unmerged after this step: merging them gives an invalid solid
        with BuildSketch(Plane(origin=(0, 8, 0), x_dir=(1, 0, 0), z_dir=(0, 1, 0))):
            with Locations(Location((-114, 34, 0), (0, 0, 270))):
                Circle(MIRRORED_LUG_BOLT_HOLE_SKETCH_R)
        extrude(amount=-MIRRORED_LUG_BOLT_HOLE_DEPTH, mode=Mode.SUBTRACT)


solid = part_1.part
